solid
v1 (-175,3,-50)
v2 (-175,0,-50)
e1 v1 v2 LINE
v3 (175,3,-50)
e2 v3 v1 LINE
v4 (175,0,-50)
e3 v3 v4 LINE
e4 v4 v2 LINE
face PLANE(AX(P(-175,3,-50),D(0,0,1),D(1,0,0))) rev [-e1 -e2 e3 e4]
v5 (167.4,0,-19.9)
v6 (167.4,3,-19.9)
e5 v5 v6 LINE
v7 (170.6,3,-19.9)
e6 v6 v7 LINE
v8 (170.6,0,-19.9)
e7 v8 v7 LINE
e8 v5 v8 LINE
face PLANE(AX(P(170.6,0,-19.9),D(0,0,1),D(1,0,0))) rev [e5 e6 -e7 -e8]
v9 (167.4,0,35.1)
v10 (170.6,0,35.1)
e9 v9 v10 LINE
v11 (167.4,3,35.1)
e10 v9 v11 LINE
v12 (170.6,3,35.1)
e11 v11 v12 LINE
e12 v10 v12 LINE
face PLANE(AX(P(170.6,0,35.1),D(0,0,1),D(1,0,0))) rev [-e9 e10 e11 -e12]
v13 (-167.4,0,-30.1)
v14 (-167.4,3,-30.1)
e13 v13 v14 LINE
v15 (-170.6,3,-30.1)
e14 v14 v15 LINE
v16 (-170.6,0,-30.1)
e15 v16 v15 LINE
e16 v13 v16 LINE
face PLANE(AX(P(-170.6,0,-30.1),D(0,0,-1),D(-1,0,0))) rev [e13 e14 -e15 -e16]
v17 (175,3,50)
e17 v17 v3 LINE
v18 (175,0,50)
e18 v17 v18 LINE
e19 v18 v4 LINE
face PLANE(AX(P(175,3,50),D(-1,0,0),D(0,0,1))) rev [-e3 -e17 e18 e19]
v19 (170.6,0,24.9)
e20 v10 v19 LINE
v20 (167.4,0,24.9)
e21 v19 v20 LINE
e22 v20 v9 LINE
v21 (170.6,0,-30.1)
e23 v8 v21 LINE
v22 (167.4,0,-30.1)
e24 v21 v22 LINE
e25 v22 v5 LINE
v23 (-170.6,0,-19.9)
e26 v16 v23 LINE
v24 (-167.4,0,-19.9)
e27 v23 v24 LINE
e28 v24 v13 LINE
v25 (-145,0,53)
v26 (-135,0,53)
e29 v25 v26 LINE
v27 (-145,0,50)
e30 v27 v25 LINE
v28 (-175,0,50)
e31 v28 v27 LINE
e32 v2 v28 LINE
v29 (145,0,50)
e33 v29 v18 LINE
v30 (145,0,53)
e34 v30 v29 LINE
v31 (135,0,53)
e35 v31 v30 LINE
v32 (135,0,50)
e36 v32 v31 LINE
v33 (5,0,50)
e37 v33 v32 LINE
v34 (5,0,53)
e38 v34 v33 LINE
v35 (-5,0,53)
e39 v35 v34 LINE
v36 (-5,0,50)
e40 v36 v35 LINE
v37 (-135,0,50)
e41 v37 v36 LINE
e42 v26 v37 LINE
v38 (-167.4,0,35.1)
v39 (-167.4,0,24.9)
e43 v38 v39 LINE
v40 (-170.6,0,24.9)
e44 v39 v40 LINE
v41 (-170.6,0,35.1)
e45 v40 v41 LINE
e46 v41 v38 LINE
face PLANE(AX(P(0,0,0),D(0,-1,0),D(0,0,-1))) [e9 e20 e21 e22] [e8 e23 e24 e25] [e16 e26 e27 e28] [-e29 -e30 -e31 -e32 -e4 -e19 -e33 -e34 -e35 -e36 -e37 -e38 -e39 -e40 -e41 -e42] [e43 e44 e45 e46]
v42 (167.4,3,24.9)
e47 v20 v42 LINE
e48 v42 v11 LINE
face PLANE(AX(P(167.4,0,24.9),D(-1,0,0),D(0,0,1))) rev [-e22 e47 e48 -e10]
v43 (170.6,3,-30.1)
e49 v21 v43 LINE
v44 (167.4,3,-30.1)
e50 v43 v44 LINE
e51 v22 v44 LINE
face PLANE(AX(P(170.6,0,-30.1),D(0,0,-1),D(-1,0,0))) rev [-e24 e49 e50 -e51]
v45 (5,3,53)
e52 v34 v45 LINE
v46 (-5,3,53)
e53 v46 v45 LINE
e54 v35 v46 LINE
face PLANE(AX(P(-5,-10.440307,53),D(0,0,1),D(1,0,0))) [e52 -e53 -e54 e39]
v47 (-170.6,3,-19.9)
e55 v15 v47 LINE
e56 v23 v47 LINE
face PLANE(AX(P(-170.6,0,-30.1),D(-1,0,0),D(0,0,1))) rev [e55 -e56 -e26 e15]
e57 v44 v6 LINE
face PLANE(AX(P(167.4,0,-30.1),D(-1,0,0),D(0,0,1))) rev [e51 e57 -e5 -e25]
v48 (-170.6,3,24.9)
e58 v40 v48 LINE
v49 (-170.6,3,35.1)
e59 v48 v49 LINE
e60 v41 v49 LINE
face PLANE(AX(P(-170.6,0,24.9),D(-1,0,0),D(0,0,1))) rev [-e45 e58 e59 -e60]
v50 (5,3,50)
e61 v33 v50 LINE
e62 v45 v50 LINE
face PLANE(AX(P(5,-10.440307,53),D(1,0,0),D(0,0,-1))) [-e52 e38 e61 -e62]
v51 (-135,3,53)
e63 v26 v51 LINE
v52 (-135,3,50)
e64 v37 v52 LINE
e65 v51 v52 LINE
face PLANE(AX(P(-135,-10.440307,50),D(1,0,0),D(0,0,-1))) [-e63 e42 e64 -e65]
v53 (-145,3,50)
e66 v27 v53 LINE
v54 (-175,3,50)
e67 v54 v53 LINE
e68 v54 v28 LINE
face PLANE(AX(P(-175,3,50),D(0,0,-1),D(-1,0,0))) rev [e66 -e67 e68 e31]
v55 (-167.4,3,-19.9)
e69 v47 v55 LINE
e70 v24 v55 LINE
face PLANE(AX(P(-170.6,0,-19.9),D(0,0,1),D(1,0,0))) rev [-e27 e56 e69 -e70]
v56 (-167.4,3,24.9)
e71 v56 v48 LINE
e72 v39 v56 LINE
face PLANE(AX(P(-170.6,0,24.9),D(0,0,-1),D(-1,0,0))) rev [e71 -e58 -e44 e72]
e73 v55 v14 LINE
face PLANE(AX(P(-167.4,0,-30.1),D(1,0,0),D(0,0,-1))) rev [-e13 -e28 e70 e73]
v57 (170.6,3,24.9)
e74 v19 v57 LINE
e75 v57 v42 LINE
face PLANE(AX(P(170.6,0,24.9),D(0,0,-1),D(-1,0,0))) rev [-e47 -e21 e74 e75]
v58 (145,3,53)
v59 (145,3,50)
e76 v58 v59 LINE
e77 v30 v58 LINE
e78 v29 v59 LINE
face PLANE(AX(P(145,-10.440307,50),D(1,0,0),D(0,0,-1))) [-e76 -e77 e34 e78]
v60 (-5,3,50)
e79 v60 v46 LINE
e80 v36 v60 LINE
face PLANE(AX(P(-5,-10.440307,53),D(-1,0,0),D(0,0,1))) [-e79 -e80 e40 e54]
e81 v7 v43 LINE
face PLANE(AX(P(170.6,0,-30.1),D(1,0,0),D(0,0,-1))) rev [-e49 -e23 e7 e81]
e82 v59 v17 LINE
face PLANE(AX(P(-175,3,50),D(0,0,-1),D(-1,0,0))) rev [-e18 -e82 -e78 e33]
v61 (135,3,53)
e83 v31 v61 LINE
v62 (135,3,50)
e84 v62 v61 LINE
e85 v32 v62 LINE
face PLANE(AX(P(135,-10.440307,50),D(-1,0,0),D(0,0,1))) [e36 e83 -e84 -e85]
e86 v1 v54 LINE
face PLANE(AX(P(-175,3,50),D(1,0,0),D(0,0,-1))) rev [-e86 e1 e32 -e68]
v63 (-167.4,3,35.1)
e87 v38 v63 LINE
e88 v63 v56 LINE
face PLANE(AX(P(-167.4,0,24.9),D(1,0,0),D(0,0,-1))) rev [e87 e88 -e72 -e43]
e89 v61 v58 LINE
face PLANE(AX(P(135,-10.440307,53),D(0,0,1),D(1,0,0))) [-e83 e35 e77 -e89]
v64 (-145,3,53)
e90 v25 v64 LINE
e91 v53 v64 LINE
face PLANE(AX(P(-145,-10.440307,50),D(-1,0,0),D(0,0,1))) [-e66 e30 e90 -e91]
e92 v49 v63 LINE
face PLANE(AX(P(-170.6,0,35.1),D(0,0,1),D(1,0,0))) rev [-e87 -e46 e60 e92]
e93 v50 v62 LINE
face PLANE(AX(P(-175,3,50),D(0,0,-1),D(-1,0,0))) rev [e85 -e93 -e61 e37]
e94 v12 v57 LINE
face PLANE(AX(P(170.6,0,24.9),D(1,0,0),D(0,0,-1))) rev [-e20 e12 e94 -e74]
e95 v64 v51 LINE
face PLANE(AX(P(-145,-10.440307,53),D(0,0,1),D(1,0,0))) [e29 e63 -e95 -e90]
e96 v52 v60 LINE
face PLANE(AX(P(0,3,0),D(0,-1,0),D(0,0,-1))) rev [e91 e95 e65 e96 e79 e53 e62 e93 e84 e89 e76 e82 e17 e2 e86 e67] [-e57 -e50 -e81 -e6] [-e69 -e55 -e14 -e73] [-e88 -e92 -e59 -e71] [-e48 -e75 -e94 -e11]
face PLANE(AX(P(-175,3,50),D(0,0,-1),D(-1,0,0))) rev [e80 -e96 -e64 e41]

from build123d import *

# Parameters (mm, degrees)
SKETCH1_W           = 350
SKETCH1_H           = 100
BOSS_EXTRUDE1_DEPTH = 3
SKETCH2_W           = 3.2
SKETCH2_H           = 10.2
CUT_EXTRUDE1_DEPTH  = 183.027470454
SKETCH3_W           = 10
SKETCH3_H           = 3
BOSS_EXTRUDE2_DEPTH = 3


with BuildPart() as part:
    # Sketch1 → Boss-Extrude1 (new body)
    with BuildSketch(Plane(origin=(0, 0, 0), x_dir=(1, 0, 0), z_dir=(0, 1, 0))):
        Rectangle(SKETCH1_W, SKETCH1_H)
    extrude(amount=BOSS_EXTRUDE1_DEPTH)

    # Sketch2 → Cut-Extrude1 (cut, through all)
    with BuildSketch(Plane(origin=(0, 3, 0), x_dir=(1, 0, 0), z_dir=(0, 1, 0))):
        with Locations((-169, 25)):
            Rectangle(SKETCH2_W, SKETCH2_H)
        with Locations((-169, -30)):
            Rectangle(SKETCH2_W, SKETCH2_H)
        with Locations((169, -30)):
            Rectangle(SKETCH2_W, SKETCH2_H)
        with Locations((169, 25)):
            Rectangle(SKETCH2_W, SKETCH2_H)
    extrude(amount=-CUT_EXTRUDE1_DEPTH, mode=Mode.SUBTRACT)

    # Sketch3 → Boss-Extrude2 (add)
    with BuildSketch(Plane(origin=(0, 3, 0), x_dir=(1, 0, 0), z_dir=(0, 1, 0))):
        with Locations((-140, -51.5)):
            Rectangle(SKETCH3_W, SKETCH3_H)
        with Locations((0, -51.5)):
            Rectangle(SKETCH3_W, SKETCH3_H)
        with Locations((140, -51.5)):
            Rectangle(SKETCH3_W, SKETCH3_H)
    extrude(amount=-BOSS_EXTRUDE2_DEPTH)


solid = part.part
